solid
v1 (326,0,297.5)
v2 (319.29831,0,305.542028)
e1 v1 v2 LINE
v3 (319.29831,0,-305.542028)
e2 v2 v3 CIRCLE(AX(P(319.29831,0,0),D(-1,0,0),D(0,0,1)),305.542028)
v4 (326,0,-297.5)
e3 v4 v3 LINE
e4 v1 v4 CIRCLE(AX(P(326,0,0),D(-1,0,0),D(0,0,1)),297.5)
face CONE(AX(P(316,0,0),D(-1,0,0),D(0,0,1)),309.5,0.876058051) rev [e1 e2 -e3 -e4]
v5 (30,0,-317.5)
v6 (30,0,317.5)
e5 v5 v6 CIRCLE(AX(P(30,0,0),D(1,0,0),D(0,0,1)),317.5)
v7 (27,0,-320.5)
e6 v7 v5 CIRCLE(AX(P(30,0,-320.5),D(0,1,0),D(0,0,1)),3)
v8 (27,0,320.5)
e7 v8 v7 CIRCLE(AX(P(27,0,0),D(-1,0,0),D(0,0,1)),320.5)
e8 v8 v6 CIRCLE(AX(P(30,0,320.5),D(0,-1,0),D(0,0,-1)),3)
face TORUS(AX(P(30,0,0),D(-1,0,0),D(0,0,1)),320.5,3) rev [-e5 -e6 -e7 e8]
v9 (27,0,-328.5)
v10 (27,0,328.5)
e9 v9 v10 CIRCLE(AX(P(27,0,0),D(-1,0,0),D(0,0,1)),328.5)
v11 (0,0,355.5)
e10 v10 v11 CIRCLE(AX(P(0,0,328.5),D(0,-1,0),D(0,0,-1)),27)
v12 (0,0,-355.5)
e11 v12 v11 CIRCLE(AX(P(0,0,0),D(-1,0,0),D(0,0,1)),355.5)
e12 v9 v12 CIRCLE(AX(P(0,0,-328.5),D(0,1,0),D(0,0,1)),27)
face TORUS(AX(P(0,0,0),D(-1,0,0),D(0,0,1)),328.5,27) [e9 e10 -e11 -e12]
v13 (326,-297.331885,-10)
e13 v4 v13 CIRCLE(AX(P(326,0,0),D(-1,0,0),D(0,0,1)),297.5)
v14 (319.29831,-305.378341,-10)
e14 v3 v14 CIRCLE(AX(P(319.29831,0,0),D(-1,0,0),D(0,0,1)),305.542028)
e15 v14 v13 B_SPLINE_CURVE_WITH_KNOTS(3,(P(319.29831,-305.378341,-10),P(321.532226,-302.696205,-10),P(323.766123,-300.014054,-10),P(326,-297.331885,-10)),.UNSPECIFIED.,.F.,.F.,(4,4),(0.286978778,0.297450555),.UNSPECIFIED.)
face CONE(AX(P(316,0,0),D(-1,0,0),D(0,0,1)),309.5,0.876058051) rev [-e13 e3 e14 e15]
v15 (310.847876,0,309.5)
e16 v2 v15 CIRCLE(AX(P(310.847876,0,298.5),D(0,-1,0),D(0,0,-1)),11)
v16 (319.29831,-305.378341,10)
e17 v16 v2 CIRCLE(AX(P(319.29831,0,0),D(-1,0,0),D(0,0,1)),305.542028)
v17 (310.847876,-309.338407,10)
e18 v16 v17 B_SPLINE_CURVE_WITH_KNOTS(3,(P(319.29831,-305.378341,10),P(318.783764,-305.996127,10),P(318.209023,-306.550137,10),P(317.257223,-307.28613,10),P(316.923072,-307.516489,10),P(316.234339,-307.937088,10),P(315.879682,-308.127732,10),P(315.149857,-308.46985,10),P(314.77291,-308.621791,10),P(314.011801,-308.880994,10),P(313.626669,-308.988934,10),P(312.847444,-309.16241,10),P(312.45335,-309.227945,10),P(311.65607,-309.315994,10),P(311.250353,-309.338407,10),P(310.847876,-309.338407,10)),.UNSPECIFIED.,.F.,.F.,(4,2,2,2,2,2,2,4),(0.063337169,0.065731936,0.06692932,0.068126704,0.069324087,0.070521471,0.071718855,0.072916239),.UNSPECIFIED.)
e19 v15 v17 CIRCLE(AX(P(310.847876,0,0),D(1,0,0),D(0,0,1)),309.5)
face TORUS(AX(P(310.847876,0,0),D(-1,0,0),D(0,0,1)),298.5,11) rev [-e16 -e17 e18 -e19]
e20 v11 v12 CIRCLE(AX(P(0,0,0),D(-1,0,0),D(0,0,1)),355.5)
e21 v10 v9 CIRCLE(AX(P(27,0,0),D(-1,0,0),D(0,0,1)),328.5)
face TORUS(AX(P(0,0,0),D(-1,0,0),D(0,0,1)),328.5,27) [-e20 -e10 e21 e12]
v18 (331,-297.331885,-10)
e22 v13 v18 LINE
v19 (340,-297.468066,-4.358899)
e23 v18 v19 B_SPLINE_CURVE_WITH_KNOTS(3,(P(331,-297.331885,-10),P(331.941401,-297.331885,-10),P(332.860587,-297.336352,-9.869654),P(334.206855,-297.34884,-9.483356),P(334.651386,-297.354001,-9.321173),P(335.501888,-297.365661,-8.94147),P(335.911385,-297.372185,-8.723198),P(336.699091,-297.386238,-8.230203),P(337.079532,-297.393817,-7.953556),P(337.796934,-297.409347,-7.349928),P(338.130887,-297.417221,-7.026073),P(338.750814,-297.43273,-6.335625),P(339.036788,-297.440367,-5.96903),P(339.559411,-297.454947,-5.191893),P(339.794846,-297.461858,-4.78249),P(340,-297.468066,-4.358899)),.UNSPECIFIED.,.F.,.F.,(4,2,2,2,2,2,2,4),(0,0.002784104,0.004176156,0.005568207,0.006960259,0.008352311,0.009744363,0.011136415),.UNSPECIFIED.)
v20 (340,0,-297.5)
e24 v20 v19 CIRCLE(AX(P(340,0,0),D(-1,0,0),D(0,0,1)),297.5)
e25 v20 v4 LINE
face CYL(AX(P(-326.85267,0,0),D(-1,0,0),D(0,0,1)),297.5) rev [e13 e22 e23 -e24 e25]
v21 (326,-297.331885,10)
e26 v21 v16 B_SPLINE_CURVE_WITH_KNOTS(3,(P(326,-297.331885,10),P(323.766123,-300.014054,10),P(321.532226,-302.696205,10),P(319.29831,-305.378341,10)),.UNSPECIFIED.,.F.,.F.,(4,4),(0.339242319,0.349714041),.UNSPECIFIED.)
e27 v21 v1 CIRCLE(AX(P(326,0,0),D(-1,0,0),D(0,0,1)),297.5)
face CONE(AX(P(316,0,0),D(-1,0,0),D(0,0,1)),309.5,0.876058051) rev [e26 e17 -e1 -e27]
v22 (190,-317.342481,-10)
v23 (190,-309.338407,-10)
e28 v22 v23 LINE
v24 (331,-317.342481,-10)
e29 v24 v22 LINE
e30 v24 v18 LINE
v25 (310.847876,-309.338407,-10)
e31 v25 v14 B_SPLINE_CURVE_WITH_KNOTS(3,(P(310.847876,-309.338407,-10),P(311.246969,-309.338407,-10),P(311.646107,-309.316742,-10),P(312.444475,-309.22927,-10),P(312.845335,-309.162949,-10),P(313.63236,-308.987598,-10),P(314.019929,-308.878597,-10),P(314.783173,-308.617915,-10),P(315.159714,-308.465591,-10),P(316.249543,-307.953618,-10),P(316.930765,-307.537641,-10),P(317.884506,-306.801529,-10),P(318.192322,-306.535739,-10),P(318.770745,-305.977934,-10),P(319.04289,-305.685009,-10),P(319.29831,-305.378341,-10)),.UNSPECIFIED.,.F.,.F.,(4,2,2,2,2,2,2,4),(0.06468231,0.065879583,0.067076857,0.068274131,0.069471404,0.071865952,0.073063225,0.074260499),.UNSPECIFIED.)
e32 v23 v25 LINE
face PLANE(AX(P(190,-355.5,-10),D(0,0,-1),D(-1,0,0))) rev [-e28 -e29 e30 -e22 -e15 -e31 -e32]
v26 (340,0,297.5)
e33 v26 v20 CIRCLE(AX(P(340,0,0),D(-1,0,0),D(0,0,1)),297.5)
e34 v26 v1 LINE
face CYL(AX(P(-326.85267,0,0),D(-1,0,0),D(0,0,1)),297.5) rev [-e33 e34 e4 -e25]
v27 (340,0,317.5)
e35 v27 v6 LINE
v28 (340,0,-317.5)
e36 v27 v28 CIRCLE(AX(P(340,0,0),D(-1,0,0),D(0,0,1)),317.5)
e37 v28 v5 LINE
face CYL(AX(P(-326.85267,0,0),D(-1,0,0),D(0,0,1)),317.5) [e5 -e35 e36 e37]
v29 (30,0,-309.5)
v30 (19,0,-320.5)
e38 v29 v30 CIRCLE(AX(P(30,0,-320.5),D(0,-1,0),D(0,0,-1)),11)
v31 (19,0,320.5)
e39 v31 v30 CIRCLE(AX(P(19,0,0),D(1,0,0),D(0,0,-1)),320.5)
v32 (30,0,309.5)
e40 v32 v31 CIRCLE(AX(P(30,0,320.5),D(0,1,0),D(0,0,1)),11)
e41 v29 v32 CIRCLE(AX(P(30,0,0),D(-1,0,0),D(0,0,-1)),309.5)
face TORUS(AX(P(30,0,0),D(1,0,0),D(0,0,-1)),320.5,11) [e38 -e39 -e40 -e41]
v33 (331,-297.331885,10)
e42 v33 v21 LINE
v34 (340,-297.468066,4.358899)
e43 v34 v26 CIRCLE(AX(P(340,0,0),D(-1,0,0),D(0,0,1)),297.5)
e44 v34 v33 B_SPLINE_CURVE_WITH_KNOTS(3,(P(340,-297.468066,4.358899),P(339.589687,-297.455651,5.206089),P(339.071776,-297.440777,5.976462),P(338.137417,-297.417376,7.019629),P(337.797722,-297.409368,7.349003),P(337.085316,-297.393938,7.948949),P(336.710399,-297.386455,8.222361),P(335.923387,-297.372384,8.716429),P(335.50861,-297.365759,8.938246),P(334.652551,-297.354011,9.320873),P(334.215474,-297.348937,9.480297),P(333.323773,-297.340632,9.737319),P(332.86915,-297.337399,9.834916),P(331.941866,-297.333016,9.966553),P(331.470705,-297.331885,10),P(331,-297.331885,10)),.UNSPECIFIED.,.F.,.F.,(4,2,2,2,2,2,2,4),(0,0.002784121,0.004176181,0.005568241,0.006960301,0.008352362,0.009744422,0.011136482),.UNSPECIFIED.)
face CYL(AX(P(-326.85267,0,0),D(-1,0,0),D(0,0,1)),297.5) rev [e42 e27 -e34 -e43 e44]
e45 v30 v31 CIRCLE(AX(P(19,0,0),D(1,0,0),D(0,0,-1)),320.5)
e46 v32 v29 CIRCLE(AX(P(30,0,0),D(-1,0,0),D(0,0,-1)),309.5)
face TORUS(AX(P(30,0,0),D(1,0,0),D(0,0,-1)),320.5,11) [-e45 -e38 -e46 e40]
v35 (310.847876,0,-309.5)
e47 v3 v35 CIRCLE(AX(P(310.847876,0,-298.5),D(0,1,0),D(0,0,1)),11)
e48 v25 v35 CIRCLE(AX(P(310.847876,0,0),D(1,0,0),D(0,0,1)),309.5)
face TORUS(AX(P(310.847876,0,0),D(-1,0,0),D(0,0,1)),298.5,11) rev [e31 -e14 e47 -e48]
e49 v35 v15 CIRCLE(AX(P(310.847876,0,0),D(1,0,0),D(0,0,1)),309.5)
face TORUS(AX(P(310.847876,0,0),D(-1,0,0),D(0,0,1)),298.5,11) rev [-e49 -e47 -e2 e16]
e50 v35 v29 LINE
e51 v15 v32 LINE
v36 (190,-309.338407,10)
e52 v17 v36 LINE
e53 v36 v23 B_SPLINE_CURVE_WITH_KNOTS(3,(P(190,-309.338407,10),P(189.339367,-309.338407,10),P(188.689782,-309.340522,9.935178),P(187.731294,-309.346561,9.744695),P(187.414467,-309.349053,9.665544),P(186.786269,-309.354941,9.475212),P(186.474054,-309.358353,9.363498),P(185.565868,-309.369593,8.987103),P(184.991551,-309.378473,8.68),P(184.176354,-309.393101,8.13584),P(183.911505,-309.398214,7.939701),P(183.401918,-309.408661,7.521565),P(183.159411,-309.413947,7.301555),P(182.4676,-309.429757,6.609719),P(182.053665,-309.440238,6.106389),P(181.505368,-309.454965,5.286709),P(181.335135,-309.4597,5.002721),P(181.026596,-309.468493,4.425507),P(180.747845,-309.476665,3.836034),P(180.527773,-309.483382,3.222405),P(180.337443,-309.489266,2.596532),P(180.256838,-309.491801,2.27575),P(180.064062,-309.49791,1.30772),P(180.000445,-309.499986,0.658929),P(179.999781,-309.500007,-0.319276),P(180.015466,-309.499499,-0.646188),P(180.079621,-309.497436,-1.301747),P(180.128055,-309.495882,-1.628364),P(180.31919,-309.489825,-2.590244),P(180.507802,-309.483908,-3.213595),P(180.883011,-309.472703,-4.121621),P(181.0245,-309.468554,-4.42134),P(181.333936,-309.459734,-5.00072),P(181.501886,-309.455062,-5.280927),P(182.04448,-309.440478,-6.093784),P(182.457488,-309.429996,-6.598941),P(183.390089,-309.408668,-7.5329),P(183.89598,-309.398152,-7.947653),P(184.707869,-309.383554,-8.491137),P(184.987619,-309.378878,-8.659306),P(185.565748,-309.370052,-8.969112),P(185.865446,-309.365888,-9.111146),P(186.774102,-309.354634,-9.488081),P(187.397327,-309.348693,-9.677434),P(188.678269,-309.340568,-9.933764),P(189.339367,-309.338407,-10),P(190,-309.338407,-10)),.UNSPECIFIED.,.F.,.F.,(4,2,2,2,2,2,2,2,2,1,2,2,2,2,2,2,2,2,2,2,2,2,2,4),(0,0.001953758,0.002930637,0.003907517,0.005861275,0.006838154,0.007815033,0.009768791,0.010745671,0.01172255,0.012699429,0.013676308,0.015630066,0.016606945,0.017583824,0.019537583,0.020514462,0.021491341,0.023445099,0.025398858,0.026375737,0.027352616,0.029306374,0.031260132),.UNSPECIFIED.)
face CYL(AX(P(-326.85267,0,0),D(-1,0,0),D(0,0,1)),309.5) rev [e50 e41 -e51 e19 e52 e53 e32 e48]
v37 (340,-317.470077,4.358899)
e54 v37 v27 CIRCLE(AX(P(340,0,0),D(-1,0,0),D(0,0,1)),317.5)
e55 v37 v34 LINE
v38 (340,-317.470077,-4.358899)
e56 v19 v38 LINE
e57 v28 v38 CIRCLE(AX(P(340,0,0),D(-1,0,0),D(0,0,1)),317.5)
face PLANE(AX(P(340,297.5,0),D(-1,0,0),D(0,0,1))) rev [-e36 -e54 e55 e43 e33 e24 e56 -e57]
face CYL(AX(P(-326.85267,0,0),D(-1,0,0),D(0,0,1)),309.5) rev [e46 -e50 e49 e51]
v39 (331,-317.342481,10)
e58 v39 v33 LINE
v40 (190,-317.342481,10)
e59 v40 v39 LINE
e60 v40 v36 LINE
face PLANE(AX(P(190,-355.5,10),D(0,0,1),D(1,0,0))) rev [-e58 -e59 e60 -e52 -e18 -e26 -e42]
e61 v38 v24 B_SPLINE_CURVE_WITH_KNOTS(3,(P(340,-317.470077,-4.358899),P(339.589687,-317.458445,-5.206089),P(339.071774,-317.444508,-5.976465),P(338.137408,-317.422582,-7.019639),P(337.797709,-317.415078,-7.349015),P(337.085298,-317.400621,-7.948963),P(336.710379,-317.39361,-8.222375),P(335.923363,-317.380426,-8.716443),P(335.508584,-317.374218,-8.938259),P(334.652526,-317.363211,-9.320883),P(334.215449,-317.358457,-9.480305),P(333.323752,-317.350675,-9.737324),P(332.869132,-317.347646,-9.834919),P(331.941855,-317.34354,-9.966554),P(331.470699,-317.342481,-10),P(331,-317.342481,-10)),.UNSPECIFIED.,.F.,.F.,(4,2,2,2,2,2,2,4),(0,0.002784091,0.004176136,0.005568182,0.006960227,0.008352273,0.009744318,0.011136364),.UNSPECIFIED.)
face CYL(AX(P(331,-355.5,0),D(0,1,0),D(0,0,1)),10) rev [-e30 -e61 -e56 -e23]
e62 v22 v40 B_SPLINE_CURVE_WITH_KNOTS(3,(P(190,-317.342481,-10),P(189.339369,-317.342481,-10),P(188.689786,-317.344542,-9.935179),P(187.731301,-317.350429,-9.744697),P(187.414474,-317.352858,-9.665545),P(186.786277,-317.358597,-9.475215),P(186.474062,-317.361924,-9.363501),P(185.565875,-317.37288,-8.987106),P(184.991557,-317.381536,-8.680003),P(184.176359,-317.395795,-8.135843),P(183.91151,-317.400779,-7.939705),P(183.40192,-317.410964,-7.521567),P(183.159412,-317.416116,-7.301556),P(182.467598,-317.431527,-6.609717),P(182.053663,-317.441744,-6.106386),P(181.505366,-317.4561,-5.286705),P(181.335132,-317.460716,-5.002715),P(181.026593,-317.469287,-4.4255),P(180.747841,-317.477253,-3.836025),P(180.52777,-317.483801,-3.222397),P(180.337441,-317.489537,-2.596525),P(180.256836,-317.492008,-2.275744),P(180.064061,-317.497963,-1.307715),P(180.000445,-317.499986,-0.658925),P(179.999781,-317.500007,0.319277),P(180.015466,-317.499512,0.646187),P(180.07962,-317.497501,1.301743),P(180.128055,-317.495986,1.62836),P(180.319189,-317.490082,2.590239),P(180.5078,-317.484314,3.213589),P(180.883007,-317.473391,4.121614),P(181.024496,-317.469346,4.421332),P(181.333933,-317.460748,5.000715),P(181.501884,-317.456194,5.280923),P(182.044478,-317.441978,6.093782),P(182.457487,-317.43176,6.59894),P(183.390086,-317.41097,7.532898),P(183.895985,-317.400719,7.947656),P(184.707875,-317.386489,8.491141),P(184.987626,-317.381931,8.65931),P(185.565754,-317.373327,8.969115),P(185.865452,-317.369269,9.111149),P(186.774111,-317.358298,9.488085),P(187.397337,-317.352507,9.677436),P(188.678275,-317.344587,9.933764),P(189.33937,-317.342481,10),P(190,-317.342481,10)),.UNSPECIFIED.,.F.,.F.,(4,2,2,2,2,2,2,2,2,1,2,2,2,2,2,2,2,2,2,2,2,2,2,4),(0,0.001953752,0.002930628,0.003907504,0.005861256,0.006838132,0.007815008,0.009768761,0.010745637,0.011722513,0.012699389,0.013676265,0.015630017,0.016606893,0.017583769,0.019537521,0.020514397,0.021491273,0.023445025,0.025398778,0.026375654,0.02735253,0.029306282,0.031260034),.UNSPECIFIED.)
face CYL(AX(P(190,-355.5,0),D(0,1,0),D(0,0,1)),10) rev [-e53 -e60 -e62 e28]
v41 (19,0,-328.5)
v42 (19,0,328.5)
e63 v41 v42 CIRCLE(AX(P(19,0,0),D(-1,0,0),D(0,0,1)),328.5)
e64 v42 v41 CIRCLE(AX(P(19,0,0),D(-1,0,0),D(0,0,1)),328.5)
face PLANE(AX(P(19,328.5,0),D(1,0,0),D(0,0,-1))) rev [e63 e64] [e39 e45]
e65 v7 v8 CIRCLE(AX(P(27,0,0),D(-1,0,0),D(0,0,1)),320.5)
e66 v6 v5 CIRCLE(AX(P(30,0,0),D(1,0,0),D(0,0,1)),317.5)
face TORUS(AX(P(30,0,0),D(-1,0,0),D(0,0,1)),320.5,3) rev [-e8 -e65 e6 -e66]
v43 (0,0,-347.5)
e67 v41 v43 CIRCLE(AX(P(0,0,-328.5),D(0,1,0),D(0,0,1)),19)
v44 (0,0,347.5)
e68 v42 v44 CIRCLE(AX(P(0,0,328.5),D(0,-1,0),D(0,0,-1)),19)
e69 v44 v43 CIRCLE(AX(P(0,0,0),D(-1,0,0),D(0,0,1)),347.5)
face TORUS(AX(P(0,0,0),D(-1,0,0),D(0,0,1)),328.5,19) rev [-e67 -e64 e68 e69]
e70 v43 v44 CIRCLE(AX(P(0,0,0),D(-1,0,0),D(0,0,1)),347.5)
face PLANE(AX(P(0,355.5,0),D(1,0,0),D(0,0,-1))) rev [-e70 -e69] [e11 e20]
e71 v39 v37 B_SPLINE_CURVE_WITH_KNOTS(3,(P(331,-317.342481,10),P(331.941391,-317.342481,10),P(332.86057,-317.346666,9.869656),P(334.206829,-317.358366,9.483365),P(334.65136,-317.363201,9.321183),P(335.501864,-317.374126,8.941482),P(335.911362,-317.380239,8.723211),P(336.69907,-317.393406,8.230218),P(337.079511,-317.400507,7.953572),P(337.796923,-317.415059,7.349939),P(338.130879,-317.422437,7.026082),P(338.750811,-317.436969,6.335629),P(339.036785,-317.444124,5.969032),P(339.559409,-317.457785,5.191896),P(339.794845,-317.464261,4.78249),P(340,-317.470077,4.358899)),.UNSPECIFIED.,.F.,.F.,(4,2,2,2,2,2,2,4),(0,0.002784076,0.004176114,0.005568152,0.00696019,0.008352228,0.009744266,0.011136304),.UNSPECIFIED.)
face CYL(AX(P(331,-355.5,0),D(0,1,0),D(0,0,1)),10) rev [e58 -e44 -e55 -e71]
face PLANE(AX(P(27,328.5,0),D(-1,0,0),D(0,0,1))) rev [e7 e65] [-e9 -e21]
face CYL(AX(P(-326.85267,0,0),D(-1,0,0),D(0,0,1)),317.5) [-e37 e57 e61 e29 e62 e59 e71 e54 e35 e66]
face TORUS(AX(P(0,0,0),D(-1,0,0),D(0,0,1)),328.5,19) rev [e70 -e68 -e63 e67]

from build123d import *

# Parameters (mm, degrees)
FILLET_2_R          = 11
FILLET_3_R          = 3
CUT_EXTRUDE_3_DEPTH = 607.927096175


with BuildPart() as part:
    # 草图1 → 旋转1 (revolve)
    with BuildSketch(Plane.XY, mode=Mode.PRIVATE) as revolve_1_sk:
        with BuildLine():
            Line((19, 328.5), (19, 309.5))
            Line((19, 309.5), (316, 309.5))
            Line((316, 309.5), (326, 297.5))
            Line((326, 297.5), (340, 297.5))
            Line((340, 297.5), (340, 317.5))
            Line((340, 317.5), (27, 317.5))
            Line((27, 317.5), (27, 328.5))
            ThreePointArc((27, 328.5), (19.091883092, 347.591883092), (0, 355.5))
            Line((0, 355.5), (0, 347.5))
            ThreePointArc((0, 347.5), (13.435028843, 341.935028843), (19, 328.5))
        make_face()
    revolve(revolve_1_sk.sketch.rotate(Axis((-326.852669965, 0, 0), (1, 0, 0)), 90), axis=Axis((-326.852669965, 0, 0), (1, 0, 0)))

    # 圆角2
    fillet_2_edges = [part.edges().sort_by_distance(p)[0] for p in [
        (316, 0, -309.5),
        (19, 0, -309.5),
    ]]
    fillet(fillet_2_edges, radius=FILLET_2_R)

    # 圆角3
    fillet_3_edges = [part.edges().sort_by_distance(p)[0] for p in [
        (27, 0, -317.5),
    ]]
    fillet(fillet_3_edges, radius=FILLET_3_R)

    # 草图2 → 切除-拉伸3 (cut, through all)
    with BuildSketch(Plane(origin=(0, 0, 0), x_dir=(1, 0, 0), z_dir=(0, 1, 0))):
        with BuildLine():
            Line((190, 10), (331, 10))
            ThreePointArc((331, 10), (341, 0), (331, -10))
            Line((331, -10), (190, -10))
            ThreePointArc((190, -10), (180, 0), (190, 10))
        make_face()
    extrude(amount=-CUT_EXTRUDE_3_DEPTH, mode=Mode.SUBTRACT)


solid = part.part
